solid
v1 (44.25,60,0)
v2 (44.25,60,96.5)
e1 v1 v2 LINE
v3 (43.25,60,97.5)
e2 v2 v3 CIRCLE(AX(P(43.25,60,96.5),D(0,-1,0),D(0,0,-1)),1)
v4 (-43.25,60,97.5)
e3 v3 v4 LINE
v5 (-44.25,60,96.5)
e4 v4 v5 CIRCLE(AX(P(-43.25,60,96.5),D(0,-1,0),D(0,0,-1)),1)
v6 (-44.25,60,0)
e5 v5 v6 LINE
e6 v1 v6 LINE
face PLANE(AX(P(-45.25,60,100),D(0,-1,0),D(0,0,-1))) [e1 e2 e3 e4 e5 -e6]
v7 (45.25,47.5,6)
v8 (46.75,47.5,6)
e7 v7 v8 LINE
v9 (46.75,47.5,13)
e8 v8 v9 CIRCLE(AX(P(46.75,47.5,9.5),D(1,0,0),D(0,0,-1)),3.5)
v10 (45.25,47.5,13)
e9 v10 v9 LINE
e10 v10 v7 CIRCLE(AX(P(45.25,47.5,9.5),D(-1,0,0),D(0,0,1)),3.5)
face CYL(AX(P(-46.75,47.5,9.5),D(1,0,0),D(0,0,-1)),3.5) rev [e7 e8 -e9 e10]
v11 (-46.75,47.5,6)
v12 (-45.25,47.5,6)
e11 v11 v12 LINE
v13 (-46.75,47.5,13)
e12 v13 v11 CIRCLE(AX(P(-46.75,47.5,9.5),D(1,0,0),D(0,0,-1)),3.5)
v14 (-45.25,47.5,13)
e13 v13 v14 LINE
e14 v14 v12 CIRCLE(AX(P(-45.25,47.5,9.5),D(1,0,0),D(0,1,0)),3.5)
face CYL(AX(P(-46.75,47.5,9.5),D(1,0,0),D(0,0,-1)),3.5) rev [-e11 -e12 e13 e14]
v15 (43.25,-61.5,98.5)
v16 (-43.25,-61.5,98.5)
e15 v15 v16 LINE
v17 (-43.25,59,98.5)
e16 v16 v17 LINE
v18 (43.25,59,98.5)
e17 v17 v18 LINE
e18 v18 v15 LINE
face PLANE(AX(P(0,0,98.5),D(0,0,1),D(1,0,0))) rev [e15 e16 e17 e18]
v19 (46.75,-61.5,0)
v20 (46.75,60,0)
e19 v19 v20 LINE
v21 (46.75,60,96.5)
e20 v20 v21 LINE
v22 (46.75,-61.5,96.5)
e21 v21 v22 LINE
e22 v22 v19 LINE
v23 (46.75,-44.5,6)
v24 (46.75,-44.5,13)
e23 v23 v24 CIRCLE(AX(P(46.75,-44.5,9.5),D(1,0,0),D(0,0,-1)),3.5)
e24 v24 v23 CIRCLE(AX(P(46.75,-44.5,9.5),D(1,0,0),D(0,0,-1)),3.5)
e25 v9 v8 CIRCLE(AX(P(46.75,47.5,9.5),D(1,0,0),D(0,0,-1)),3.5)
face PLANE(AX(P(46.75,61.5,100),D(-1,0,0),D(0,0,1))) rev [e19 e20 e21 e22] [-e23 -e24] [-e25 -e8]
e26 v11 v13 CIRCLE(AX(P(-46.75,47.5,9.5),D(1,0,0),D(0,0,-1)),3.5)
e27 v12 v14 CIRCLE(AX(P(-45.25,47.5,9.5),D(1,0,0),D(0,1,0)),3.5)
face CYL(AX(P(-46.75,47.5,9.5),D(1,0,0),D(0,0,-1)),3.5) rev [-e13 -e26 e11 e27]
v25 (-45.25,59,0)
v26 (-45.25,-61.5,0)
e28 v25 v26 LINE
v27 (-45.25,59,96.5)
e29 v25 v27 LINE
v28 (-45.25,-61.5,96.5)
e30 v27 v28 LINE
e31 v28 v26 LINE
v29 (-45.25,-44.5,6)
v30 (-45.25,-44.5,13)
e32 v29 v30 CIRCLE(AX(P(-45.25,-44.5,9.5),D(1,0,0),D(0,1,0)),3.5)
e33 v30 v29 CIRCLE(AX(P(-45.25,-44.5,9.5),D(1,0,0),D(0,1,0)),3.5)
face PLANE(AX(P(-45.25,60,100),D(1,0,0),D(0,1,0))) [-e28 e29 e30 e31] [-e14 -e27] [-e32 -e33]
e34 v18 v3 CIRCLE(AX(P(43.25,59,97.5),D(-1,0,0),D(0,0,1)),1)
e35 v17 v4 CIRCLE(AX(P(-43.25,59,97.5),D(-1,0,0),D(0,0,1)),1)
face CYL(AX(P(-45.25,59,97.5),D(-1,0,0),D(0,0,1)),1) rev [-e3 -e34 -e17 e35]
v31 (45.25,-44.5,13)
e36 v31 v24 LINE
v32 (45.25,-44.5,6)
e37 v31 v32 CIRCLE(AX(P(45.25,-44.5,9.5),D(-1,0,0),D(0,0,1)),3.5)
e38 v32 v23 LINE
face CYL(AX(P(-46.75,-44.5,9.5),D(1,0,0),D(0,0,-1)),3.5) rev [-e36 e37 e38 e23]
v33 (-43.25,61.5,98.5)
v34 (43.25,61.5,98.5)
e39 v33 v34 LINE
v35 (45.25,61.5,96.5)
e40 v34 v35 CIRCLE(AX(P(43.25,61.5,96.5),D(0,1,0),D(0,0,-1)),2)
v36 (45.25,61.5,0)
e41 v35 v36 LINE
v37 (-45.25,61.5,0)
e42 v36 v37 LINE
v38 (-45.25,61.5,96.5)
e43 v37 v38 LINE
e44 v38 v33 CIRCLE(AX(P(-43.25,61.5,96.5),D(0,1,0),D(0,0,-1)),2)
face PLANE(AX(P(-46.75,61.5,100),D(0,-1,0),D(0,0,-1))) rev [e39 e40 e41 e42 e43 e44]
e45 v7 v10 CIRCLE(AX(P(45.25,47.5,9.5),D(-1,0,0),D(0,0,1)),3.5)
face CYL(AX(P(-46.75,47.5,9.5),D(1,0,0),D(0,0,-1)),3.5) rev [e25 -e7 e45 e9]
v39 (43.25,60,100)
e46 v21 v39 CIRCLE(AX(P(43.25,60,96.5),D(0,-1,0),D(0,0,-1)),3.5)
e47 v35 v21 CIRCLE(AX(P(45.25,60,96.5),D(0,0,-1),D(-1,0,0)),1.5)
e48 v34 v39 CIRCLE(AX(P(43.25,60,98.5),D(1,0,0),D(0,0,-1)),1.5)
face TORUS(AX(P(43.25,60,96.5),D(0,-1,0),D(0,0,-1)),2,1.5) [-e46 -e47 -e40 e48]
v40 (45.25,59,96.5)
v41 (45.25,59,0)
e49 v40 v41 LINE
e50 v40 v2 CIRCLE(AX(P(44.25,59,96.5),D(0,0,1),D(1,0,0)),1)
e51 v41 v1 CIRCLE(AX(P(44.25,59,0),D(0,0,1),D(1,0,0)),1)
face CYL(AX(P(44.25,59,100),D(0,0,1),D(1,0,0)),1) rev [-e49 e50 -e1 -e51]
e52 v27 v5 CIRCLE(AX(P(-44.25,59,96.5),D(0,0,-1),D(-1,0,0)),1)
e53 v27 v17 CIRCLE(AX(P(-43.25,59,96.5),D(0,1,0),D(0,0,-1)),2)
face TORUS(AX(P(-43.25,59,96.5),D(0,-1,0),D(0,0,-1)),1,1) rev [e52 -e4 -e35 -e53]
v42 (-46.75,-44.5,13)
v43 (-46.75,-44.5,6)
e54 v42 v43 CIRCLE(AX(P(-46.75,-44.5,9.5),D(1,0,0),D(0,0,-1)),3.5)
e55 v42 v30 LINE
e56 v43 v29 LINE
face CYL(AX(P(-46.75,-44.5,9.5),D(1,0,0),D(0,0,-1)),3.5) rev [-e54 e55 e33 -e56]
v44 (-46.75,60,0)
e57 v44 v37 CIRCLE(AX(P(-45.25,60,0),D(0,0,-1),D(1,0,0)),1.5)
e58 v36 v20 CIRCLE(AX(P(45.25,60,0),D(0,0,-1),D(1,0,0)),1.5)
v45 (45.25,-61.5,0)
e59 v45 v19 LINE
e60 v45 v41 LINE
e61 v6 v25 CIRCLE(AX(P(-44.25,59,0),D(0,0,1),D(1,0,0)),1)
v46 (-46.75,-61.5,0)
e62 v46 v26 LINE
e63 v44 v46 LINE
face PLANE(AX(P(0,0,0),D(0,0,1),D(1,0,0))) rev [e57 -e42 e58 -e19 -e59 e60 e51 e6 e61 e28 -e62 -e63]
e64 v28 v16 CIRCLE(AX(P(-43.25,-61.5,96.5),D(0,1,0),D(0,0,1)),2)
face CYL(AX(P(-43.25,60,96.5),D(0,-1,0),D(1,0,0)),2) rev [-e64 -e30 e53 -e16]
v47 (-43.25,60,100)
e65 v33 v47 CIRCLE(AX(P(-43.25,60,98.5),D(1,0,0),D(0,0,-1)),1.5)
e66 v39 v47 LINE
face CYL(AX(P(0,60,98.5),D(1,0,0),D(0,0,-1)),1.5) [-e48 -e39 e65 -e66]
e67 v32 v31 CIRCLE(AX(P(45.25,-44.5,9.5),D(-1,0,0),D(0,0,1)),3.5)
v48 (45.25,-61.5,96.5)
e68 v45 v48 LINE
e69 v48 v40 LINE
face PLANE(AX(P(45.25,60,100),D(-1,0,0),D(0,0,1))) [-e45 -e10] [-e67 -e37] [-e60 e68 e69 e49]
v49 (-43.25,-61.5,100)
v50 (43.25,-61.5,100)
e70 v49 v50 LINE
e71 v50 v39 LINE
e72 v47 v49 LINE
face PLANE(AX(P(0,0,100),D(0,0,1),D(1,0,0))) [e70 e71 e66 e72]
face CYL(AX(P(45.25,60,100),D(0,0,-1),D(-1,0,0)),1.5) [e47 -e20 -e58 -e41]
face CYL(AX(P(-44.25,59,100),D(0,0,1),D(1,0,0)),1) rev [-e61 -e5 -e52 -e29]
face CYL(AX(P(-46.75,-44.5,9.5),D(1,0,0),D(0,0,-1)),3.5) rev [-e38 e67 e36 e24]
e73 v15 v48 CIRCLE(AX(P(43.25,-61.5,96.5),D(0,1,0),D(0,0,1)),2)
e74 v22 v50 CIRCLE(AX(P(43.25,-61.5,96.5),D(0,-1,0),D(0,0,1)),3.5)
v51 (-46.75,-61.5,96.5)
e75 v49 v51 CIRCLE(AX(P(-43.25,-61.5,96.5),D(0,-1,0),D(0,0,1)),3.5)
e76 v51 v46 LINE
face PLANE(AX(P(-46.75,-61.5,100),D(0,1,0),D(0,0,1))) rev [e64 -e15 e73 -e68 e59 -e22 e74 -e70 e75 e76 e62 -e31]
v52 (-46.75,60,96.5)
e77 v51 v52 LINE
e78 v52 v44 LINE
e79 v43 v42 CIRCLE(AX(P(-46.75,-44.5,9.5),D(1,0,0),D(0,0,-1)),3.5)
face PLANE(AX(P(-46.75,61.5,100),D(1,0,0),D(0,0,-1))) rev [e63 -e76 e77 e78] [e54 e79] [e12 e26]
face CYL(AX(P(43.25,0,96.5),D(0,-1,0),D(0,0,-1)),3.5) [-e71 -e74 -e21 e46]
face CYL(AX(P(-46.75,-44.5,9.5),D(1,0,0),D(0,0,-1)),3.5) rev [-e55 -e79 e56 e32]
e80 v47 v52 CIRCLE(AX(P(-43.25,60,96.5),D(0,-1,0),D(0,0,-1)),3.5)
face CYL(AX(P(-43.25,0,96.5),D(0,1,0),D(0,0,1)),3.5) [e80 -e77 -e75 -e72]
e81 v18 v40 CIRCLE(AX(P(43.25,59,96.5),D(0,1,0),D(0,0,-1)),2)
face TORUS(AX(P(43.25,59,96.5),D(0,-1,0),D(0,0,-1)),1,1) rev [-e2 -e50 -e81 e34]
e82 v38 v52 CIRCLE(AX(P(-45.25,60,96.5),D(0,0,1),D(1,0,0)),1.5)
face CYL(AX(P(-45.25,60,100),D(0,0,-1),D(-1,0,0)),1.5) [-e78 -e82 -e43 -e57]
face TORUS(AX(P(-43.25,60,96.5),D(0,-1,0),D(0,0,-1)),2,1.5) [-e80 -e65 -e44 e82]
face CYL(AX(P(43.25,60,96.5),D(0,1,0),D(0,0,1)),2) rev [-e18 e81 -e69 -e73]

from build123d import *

# Parameters (mm, degrees)
SKETCH_1_W          = 93.5
SKETCH_1_H          = 123
SKETCH_1_W_2        = 90.5
SKETCH_1_H_2        = 120
EXTRUDE_1_DEPTH     = 100
SKETCH_2_W          = 93.5
SKETCH_2_H          = 123
EXTRUDE_2_DEPTH     = 1.5
SKETCH_3_W          = 90.5
SKETCH_3_H          = 98.5
CUT_EXTRUDE_1_DEPTH = 3
SKETCH_4_R          = 3.5
CUT_EXTRUDE_2_DEPTH = 151.081644447
FILLET_1_R          = 2
FILLET_2_R          = 3.5
FILLET_3_R          = 1
FILLET_4_R          = 1.5


with BuildPart() as part:
    # 草图1 → 凸台-拉伸1 (new body)
    with BuildSketch(Plane.XY):
        Rectangle(SKETCH_1_W, SKETCH_1_H)
        Rectangle(SKETCH_1_W_2, SKETCH_1_H_2, mode=Mode.SUBTRACT)
    extrude(amount=EXTRUDE_1_DEPTH)

    # 草图2 → 凸台-拉伸2 (add)
    with BuildSketch(Plane.XY.offset(100)):
        Rectangle(SKETCH_2_W, SKETCH_2_H)
    extrude(amount=-EXTRUDE_2_DEPTH)

    # 草图3 → 切除-拉伸1 (cut)
    with BuildSketch(Plane.XZ.offset(61.5)):
        with Locations((0, 49.25)):
            Rectangle(SKETCH_3_W, SKETCH_3_H)
    extrude(amount=-CUT_EXTRUDE_1_DEPTH, mode=Mode.SUBTRACT)

    # 草图4 → 切除-拉伸2 (cut, through all)
    with BuildSketch(Plane(origin=(46.75, 0, 0), x_dir=(0, 0, -1), z_dir=(1, 0, 0))):
        with Locations((-9.5, -44.5)):
            Circle(SKETCH_4_R)
        with Locations((-9.5, 47.5)):
            Circle(SKETCH_4_R)
    extrude(amount=-CUT_EXTRUDE_2_DEPTH, mode=Mode.SUBTRACT)

    # 圆角1
    fillet_1_edges = [part.edges().sort_by_distance(p)[0] for p in [
        (45.25, -0.75, 98.5),
        (-45.25, -0.75, 98.5),
    ]]
    fillet(fillet_1_edges, radius=FILLET_1_R)

    # 圆角2
    fillet_2_edges = [part.edges().sort_by_distance(p)[0] for p in [
        (-46.75, 0, 100),
        (46.75, 0, 100),
    ]]
    fillet(fillet_2_edges, radius=FILLET_2_R)

    # 圆角3
    fillet_3_edges = [part.edges().sort_by_distance(p)[0] for p in [
        (-45.25, 60, 48.25),
        (0, 60, 98.5),
        (45.25, 60, 48.25),
        (44.664213562, 60, 97.914213562),
        (-44.664213562, 60, 97.914213562),
    ]]
    fillet(fillet_3_edges, radius=FILLET_3_R)

    # 圆角4
    fillet_4_edges = [part.edges().sort_by_distance(p)[0] for p in [
        (46.75, 61.5, 48.25),
        (-46.75, 61.5, 48.25),
        (-45.724873734, 61.5, 98.974873734),
        (45.724873734, 61.5, 98.974873734),
        (0, 61.5, 100),
    ]]
    fillet(fillet_4_edges, radius=FILLET_4_R)


solid = part.part
